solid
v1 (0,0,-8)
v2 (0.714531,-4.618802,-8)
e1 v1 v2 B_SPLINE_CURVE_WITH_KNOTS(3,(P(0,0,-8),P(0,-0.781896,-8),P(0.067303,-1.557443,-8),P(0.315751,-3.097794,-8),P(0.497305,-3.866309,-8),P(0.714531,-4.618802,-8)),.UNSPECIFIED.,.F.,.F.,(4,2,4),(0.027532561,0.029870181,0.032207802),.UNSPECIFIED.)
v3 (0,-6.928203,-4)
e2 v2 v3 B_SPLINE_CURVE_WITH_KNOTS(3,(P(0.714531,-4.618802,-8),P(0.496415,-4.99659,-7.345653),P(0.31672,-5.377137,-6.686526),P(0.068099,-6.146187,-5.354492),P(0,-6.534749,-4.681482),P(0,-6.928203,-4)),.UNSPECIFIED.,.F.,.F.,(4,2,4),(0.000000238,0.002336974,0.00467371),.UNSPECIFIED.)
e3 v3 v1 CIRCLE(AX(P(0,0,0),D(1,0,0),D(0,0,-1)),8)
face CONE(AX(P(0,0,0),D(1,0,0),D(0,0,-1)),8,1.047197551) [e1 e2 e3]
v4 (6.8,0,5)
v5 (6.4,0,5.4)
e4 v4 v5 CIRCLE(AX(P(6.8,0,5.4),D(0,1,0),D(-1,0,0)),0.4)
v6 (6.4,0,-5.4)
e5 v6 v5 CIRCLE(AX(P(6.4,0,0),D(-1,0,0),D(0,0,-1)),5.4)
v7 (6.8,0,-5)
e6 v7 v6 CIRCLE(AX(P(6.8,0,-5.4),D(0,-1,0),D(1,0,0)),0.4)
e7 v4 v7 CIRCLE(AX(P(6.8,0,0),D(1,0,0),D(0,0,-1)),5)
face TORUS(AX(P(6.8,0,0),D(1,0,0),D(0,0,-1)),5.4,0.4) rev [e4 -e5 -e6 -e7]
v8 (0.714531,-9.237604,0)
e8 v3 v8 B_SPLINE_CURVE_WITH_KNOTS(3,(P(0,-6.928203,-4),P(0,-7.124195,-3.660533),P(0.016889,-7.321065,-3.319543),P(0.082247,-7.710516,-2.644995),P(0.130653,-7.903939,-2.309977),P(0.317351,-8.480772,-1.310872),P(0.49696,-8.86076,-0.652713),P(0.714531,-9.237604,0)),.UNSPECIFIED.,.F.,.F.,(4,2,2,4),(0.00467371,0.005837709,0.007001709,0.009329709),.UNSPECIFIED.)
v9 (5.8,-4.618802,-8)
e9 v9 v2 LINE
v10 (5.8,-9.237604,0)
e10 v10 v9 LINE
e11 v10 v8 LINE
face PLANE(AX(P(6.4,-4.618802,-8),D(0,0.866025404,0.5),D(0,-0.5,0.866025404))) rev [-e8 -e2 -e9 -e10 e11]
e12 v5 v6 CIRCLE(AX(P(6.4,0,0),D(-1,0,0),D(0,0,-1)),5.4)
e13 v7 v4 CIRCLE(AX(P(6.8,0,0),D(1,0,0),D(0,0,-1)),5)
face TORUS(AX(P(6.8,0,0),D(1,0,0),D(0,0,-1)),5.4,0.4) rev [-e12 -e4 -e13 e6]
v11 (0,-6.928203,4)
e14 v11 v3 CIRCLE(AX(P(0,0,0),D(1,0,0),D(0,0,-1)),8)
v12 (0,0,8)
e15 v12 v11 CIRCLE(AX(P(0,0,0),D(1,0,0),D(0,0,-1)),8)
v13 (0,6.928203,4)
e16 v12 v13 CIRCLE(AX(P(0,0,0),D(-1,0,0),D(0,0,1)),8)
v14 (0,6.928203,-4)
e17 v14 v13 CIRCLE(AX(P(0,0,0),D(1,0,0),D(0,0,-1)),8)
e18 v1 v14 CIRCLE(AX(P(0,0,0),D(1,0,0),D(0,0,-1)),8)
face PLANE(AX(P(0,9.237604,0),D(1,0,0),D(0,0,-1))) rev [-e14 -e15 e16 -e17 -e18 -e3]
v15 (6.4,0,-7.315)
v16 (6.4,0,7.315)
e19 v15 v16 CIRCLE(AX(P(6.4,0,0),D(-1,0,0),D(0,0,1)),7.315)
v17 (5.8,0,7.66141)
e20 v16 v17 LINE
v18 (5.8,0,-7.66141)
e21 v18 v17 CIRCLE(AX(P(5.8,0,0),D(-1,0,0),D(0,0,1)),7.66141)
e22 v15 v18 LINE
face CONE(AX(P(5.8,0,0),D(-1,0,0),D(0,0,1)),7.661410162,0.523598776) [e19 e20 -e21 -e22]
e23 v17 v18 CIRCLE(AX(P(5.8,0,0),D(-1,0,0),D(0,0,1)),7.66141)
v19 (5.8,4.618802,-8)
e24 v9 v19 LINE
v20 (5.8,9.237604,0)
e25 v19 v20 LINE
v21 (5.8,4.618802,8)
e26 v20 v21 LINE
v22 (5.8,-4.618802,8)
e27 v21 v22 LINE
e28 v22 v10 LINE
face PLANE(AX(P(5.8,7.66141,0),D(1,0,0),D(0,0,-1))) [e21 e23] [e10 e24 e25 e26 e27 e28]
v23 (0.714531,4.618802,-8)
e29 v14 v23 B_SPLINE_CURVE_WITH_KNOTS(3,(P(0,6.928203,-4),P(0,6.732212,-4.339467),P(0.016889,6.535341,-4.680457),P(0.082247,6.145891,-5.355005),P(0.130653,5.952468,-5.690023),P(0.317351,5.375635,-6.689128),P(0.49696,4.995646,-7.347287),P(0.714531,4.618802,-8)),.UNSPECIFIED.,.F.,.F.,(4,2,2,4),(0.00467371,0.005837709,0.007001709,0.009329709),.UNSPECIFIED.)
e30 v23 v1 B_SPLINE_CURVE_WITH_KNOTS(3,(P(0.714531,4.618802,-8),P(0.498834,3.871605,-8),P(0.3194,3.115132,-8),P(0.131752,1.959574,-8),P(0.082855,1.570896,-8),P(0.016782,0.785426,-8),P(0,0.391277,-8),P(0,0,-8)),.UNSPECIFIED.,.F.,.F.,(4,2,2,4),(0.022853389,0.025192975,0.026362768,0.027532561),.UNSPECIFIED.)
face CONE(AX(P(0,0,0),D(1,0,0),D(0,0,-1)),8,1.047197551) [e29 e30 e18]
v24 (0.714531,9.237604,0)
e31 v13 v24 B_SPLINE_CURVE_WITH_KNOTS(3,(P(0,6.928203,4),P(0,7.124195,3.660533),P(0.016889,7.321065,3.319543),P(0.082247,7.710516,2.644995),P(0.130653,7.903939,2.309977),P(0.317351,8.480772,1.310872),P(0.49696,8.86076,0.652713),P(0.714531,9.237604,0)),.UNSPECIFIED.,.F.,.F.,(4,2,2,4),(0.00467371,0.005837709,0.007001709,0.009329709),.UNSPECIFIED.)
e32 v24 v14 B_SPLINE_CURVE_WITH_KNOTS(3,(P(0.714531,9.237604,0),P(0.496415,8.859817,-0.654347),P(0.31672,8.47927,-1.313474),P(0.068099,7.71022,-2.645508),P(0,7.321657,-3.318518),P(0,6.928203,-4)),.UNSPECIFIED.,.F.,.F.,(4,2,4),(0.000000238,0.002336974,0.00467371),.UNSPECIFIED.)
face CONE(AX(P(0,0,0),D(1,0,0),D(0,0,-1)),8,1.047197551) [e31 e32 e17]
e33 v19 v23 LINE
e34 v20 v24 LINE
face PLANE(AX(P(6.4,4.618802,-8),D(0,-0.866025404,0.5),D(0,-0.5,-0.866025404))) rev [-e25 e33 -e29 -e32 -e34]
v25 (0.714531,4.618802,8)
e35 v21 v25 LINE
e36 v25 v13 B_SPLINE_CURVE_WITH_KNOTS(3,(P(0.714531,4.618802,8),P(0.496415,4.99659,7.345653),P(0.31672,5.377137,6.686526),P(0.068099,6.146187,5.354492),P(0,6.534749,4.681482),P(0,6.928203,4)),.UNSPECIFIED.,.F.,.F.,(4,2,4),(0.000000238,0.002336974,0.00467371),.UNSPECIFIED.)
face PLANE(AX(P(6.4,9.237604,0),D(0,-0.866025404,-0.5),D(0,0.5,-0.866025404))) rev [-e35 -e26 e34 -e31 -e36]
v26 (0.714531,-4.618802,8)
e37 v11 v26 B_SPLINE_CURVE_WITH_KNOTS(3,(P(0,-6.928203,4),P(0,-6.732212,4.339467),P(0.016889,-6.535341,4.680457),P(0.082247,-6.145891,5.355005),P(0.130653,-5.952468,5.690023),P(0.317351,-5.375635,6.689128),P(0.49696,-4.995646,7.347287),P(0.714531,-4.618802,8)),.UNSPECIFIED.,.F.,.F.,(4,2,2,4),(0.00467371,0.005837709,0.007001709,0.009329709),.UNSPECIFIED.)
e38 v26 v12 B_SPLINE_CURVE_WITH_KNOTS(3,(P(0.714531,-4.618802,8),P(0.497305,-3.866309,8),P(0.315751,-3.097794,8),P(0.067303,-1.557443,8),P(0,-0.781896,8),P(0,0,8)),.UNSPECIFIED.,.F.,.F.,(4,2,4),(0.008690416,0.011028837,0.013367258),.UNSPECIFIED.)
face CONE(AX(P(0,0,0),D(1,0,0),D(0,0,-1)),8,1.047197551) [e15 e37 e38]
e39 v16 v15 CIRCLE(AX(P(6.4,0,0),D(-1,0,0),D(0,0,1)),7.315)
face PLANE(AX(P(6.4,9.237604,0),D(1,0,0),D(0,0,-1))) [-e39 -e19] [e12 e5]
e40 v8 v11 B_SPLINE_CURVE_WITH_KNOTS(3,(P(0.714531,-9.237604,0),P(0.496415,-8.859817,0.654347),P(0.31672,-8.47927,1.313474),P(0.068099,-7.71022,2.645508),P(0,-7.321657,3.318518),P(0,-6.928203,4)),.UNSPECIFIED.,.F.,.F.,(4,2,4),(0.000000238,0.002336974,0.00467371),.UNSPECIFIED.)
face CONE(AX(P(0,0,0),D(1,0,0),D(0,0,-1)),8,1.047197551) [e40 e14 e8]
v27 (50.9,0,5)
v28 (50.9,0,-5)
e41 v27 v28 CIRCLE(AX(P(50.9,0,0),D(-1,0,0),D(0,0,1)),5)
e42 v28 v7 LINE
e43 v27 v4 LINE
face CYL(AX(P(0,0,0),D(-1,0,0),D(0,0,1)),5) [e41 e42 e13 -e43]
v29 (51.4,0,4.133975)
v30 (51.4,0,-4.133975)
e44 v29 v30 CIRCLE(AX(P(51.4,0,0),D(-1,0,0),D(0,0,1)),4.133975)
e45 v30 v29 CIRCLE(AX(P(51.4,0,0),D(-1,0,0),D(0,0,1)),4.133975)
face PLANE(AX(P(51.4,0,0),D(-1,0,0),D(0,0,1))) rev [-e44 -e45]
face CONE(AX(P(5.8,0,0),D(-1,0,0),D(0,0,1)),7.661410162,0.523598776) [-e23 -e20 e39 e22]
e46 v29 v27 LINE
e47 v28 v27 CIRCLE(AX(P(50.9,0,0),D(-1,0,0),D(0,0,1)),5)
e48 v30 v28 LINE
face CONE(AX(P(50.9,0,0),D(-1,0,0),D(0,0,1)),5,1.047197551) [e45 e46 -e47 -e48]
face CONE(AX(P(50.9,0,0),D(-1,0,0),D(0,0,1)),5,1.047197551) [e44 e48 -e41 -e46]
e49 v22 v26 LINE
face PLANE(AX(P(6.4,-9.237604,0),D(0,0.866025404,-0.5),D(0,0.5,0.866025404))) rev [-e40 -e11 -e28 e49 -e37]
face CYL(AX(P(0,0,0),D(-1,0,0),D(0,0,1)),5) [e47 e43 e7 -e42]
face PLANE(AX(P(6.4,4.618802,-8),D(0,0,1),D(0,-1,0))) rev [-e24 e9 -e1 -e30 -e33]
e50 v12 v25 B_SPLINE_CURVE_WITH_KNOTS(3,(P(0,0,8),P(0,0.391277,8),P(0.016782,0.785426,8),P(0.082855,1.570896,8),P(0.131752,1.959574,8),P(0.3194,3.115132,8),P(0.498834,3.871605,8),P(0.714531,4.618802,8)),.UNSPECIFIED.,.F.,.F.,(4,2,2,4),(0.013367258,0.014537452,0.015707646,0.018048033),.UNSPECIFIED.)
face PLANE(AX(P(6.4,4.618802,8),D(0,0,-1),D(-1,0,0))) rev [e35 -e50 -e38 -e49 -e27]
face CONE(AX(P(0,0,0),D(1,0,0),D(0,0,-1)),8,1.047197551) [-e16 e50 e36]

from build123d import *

# Parameters (mm, degrees)
EXTRUDE_419_DEPTH = 6.4
FILLET_1345_R     = 0.4


with BuildPart() as part:
    # 草图1 → Extrude 419 (new body)
    with BuildSketch(Plane(origin=(0, 0, 0), x_dir=(0, 0, -1), z_dir=(1, 0, 0))):
        Polygon((8, 4.618802154), (8, -4.618802154), (0, -9.237604307), (-8, -4.618802154), (-8, 4.618802154), (0, 9.237604307), align=None)
    extrude(amount=EXTRUDE_419_DEPTH)

    # 草图2 → 凸台-旋转1 (revolve)
    with BuildSketch(Plane.XY, mode=Mode.PRIVATE) as revolve_1_sk:
        Polygon((0, 0), (51.4, 0), (51.4, 4.134), (51.4, 5), (25.7, 5), (0, 5), align=None)
    revolve(revolve_1_sk.sketch.rotate(Axis((0, 0, 0), (1, 0, 0)), 90), axis=Axis((0, 0, 0), (1, 0, 0)))

    # 草图3 → 切除-旋转1 (revolve, cut)
    with BuildSketch(Plane.XY):
        Polygon((0, 8), (3.601282526, 14.237604307), (3.601282526, 19.237604307), (-10, 19.237604307), (-10, 8), align=None)
    revolve(axis=Axis((0, 0, 0), (1, 0, 0)), mode=Mode.SUBTRACT)

    # 草图4 → 切除-旋转3 (revolve, cut)
    with BuildSketch(Plane.XY, mode=Mode.PRIVATE) as cut_revolve_3_sk:
        Polygon((6.4, 7.315), (5.8, 7.661410162), (5.8, 9.237604307), (6.4, 9.237604307), align=None)
    revolve(cut_revolve_3_sk.sketch.rotate(Axis((0, 0, 0), (1, 0, 0)), 90), axis=Axis((0, 0, 0), (1, 0, 0)), mode=Mode.SUBTRACT)

    # Fillet 1345
    fillet_1345_edges = [part.edges().sort_by_distance(p)[0] for p in [
        (6.4, 0, -5),
    ]]
    fillet(fillet_1345_edges, radius=FILLET_1345_R)

    # 草图6 → 切除-旋转4 (revolve, cut)
    with BuildSketch(Plane.XY, mode=Mode.PRIVATE) as cut_revolve_4_sk:
        Polygon((50.9, 5), (51.9, 5), (51.4, 4.133974596), align=None)
    revolve(cut_revolve_4_sk.sketch.rotate(Axis((0, 0, 0), (1, 0, 0)), 90), axis=Axis((0, 0, 0), (1, 0, 0)), mode=Mode.SUBTRACT)


solid = part.part
